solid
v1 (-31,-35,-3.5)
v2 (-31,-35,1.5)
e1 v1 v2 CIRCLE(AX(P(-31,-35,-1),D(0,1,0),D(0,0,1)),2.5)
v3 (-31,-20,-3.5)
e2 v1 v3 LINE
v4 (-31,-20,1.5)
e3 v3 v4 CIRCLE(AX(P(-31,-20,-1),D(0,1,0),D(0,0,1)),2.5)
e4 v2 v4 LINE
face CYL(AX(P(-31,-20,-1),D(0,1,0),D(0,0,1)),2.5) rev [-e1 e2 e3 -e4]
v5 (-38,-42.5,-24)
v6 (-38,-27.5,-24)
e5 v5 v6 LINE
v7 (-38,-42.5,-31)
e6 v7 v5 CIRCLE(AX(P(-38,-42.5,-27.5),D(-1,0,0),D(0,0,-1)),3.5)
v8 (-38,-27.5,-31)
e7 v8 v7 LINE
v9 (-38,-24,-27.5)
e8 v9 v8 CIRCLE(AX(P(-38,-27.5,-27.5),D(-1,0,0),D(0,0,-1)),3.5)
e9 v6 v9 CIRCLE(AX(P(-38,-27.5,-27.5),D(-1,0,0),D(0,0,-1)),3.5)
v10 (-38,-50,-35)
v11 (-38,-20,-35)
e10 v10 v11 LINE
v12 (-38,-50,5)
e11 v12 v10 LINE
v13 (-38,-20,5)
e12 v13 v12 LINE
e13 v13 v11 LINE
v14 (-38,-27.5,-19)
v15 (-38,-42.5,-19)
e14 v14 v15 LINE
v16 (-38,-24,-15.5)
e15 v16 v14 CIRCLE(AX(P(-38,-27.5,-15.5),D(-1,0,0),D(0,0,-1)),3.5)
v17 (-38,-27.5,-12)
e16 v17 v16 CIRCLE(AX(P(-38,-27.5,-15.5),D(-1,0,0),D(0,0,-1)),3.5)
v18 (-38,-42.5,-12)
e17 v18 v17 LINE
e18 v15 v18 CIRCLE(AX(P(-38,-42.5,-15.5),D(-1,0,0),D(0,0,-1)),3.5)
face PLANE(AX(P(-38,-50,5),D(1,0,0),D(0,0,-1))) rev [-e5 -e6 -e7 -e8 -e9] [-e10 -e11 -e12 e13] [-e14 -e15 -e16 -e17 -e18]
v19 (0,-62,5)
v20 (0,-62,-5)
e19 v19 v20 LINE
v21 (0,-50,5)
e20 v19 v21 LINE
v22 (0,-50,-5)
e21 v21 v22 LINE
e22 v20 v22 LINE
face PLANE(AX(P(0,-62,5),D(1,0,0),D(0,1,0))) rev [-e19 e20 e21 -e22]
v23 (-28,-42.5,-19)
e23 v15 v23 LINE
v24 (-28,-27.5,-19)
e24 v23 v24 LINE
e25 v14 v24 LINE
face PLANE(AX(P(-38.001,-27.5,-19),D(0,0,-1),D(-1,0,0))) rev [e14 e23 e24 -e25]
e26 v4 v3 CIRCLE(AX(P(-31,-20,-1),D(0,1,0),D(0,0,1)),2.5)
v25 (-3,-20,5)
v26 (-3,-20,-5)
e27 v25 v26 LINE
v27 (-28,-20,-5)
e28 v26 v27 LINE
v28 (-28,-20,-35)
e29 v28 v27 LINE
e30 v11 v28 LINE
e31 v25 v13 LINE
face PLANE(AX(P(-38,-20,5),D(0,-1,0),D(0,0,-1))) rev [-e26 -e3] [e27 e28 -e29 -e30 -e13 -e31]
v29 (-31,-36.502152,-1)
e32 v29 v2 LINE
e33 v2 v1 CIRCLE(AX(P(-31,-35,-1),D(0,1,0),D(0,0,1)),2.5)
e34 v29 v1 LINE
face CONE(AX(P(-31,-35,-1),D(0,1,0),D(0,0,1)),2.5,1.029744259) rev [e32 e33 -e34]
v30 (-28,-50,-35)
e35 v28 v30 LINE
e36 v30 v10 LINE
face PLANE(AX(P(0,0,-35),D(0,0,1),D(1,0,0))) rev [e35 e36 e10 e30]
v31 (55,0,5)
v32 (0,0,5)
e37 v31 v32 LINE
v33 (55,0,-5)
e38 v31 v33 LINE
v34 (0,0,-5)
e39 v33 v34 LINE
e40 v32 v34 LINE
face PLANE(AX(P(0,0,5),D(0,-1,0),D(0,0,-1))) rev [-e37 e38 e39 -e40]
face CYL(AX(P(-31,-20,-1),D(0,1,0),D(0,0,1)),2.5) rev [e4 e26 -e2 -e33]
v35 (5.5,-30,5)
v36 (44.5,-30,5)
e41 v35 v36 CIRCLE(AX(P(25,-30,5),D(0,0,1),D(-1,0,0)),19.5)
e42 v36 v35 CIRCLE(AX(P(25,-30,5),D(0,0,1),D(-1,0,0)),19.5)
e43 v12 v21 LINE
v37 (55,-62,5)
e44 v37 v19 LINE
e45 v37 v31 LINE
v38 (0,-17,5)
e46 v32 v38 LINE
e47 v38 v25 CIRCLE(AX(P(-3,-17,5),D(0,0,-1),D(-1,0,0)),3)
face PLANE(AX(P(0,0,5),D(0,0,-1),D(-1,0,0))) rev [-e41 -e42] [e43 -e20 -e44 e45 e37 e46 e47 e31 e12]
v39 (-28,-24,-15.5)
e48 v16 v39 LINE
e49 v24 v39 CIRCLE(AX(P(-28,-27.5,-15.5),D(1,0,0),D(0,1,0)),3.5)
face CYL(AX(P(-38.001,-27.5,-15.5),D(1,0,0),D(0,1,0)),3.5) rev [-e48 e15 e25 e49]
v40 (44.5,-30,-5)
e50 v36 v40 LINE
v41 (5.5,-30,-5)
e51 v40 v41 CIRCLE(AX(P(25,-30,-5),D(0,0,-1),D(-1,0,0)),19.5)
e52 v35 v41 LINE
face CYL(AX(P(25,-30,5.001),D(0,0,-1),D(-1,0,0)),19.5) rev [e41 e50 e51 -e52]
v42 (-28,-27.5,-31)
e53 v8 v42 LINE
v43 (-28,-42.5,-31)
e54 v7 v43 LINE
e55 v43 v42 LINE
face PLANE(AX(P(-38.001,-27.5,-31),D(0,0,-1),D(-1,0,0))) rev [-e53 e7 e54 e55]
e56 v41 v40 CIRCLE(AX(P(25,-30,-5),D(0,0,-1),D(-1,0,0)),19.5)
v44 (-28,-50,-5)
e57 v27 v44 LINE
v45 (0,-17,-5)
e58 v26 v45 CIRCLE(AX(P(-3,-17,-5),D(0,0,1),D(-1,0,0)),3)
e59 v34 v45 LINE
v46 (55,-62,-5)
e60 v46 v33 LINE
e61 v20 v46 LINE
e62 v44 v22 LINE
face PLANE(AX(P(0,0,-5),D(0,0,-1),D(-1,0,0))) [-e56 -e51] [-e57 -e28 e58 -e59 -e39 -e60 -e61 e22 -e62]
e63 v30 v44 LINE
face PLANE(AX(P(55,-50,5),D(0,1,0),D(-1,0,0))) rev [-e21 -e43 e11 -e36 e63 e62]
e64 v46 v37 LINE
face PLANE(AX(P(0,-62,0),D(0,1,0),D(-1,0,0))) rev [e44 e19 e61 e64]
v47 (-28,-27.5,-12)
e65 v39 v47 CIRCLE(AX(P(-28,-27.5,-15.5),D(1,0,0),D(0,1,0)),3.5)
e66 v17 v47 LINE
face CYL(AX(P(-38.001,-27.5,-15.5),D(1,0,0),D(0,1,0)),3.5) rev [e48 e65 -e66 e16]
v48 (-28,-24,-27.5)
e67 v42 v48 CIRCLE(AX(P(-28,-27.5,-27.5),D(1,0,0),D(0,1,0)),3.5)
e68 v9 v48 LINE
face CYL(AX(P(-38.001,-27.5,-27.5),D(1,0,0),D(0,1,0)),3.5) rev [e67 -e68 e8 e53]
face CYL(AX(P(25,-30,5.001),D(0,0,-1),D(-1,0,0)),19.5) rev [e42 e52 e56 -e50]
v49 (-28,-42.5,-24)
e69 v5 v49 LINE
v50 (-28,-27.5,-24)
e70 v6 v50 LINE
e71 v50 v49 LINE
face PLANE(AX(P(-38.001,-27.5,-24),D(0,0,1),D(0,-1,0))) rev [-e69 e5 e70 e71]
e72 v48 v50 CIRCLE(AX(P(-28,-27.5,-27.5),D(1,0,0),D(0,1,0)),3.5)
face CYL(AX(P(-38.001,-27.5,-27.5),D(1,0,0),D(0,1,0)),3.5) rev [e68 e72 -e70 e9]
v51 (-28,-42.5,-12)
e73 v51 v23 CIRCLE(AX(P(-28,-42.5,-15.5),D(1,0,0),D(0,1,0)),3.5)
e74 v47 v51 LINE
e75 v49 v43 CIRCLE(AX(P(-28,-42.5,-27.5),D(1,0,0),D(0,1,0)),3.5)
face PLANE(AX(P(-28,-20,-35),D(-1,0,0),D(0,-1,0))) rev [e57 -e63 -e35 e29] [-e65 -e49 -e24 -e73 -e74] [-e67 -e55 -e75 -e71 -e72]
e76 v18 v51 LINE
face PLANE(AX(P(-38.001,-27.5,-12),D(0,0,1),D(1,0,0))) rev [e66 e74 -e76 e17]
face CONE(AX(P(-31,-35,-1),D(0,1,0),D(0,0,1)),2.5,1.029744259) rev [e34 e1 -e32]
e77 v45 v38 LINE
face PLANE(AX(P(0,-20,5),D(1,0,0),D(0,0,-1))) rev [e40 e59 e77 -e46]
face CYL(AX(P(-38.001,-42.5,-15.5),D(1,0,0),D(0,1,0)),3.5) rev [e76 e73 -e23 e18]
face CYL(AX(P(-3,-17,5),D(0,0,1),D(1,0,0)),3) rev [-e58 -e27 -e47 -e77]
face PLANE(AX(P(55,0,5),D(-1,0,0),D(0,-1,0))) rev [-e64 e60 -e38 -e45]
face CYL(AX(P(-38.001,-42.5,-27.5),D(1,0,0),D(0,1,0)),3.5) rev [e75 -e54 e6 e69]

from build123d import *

# Parameters (mm, degrees)
EXTRUDE_1_DEPTH        = 5
FILLET_1_R             = 3
CUT_EXTRUDE_1_REACH    = 77
SKETCH_2_R             = 19.5
SKETCH_4_W             = 10
SKETCH_4_H             = 30
EXTRUDE_2_DEPTH        = 30
CUT_EXTRUDE_3_REACH    = 105.024
HOLE_WIZARD_M6_1_D     = 5
HOLE_WIZARD_M6_1_DEPTH = 15
HOLE_WIZARD_M6_1_TIP   = 1.502151548
SKETCH_7_W             = 55
SKETCH_7_H             = 10
EXTRUDE_3_DEPTH        = 12


with BuildPart() as part:
    # 草图1 → 凸台-拉伸1 (new, symmetric)
    with BuildSketch(Plane.XY):
        Polygon((0, 0), (55, 0), (55, -50), (-38, -50), (-38, -20), (0, -20), align=None)
    extrude(amount=EXTRUDE_1_DEPTH, both=True)

    # 圆角1
    fillet_1_edges = [part.edges().sort_by_distance(p)[0] for p in [
        (0, -20, 0),
    ]]
    fillet(fillet_1_edges, radius=FILLET_1_R)

    # 草图2 → 切除-拉伸1 (cut, up to next)
    with BuildSketch(Plane(origin=(0, 0, -5), x_dir=(-1, 0, 0), z_dir=(0, 0, -1)), mode=Mode.PRIVATE) as cut_extrude_1_sk1:
        with Locations((-25, -30)):
            Circle(SKETCH_2_R)
    cut_extrude_1_tool1 = extrude(cut_extrude_1_sk1.sketch, amount=-CUT_EXTRUDE_1_REACH, mode=Mode.PRIVATE) & part.part
    add(cut_extrude_1_tool1.solids().sort_by_distance((25, -30, -5))[0], mode=Mode.SUBTRACT)

    # 草图4 → 凸台-拉伸2 (add)
    with BuildSketch(Plane(origin=(0, 0, -5), x_dir=(-1, 0, 0), z_dir=(0, 0, -1))):
        with Locations((33, -35)):
            Rectangle(SKETCH_4_W, SKETCH_4_H)
    extrude(amount=EXTRUDE_2_DEPTH)

    # 草图5 → 切除-拉伸3 (cut, up to next)
    with BuildSketch(Plane(origin=(-28, 0, 0), x_dir=(0, 0, -1), z_dir=(1, 0, 0)), mode=Mode.PRIVATE) as cut_extrude_3_sk1:
        with BuildLine():
            Line((31, -27.5), (31, -42.5))
            ThreePointArc((31, -42.5), (27.5, -46), (24, -42.5))
            Line((24, -42.5), (24, -27.5))
            ThreePointArc((24, -27.5), (27.5, -24), (31, -27.5))
        make_face()
    cut_extrude_3_tool1 = extrude(cut_extrude_3_sk1.sketch, amount=-CUT_EXTRUDE_3_REACH, mode=Mode.PRIVATE) & part.part
    # 草图5 → 切除-拉伸3 (cut, up to next)
    with BuildSketch(Plane(origin=(-28, 0, 0), x_dir=(0, 0, -1), z_dir=(1, 0, 0)), mode=Mode.PRIVATE) as cut_extrude_3_sk2:
        with BuildLine():
            Line((19, -27.5), (19, -42.5))
            ThreePointArc((19, -42.5), (15.5, -46), (12, -42.5))
            Line((12, -42.5), (12, -27.5))
            ThreePointArc((12, -27.5), (15.5, -24), (19, -27.5))
        make_face()
    cut_extrude_3_tool2 = extrude(cut_extrude_3_sk2.sketch, amount=-CUT_EXTRUDE_3_REACH, mode=Mode.PRIVATE) & part.part
    add(cut_extrude_3_tool1.solids().sort_by_distance((-28, -35, -27.5))[0], mode=Mode.SUBTRACT)
    add(cut_extrude_3_tool2.solids().sort_by_distance((-28, -35, -15.5))[0], mode=Mode.SUBTRACT)

    # M6 螺纹孔1
    with Locations(Plane(origin=(-31, -20, -1), x_dir=(0, 0, 1), z_dir=(0, 1, 0))):
        with Locations((0, 0)):
            Hole(HOLE_WIZARD_M6_1_D / 2, depth=HOLE_WIZARD_M6_1_DEPTH)
            with Locations((0, 0, -(HOLE_WIZARD_M6_1_DEPTH + HOLE_WIZARD_M6_1_TIP / 2))):  # 118° drill point
                Cone(0, HOLE_WIZARD_M6_1_D / 2, HOLE_WIZARD_M6_1_TIP, mode=Mode.SUBTRACT)

    # 草图7 → 凸台-拉伸3 (add)
    with BuildSketch(Plane.XZ.offset(50)):
        with Locations((27.5, 0)):
            Rectangle(SKETCH_7_W, SKETCH_7_H)
    extrude(amount=EXTRUDE_3_DEPTH)


solid = part.part
